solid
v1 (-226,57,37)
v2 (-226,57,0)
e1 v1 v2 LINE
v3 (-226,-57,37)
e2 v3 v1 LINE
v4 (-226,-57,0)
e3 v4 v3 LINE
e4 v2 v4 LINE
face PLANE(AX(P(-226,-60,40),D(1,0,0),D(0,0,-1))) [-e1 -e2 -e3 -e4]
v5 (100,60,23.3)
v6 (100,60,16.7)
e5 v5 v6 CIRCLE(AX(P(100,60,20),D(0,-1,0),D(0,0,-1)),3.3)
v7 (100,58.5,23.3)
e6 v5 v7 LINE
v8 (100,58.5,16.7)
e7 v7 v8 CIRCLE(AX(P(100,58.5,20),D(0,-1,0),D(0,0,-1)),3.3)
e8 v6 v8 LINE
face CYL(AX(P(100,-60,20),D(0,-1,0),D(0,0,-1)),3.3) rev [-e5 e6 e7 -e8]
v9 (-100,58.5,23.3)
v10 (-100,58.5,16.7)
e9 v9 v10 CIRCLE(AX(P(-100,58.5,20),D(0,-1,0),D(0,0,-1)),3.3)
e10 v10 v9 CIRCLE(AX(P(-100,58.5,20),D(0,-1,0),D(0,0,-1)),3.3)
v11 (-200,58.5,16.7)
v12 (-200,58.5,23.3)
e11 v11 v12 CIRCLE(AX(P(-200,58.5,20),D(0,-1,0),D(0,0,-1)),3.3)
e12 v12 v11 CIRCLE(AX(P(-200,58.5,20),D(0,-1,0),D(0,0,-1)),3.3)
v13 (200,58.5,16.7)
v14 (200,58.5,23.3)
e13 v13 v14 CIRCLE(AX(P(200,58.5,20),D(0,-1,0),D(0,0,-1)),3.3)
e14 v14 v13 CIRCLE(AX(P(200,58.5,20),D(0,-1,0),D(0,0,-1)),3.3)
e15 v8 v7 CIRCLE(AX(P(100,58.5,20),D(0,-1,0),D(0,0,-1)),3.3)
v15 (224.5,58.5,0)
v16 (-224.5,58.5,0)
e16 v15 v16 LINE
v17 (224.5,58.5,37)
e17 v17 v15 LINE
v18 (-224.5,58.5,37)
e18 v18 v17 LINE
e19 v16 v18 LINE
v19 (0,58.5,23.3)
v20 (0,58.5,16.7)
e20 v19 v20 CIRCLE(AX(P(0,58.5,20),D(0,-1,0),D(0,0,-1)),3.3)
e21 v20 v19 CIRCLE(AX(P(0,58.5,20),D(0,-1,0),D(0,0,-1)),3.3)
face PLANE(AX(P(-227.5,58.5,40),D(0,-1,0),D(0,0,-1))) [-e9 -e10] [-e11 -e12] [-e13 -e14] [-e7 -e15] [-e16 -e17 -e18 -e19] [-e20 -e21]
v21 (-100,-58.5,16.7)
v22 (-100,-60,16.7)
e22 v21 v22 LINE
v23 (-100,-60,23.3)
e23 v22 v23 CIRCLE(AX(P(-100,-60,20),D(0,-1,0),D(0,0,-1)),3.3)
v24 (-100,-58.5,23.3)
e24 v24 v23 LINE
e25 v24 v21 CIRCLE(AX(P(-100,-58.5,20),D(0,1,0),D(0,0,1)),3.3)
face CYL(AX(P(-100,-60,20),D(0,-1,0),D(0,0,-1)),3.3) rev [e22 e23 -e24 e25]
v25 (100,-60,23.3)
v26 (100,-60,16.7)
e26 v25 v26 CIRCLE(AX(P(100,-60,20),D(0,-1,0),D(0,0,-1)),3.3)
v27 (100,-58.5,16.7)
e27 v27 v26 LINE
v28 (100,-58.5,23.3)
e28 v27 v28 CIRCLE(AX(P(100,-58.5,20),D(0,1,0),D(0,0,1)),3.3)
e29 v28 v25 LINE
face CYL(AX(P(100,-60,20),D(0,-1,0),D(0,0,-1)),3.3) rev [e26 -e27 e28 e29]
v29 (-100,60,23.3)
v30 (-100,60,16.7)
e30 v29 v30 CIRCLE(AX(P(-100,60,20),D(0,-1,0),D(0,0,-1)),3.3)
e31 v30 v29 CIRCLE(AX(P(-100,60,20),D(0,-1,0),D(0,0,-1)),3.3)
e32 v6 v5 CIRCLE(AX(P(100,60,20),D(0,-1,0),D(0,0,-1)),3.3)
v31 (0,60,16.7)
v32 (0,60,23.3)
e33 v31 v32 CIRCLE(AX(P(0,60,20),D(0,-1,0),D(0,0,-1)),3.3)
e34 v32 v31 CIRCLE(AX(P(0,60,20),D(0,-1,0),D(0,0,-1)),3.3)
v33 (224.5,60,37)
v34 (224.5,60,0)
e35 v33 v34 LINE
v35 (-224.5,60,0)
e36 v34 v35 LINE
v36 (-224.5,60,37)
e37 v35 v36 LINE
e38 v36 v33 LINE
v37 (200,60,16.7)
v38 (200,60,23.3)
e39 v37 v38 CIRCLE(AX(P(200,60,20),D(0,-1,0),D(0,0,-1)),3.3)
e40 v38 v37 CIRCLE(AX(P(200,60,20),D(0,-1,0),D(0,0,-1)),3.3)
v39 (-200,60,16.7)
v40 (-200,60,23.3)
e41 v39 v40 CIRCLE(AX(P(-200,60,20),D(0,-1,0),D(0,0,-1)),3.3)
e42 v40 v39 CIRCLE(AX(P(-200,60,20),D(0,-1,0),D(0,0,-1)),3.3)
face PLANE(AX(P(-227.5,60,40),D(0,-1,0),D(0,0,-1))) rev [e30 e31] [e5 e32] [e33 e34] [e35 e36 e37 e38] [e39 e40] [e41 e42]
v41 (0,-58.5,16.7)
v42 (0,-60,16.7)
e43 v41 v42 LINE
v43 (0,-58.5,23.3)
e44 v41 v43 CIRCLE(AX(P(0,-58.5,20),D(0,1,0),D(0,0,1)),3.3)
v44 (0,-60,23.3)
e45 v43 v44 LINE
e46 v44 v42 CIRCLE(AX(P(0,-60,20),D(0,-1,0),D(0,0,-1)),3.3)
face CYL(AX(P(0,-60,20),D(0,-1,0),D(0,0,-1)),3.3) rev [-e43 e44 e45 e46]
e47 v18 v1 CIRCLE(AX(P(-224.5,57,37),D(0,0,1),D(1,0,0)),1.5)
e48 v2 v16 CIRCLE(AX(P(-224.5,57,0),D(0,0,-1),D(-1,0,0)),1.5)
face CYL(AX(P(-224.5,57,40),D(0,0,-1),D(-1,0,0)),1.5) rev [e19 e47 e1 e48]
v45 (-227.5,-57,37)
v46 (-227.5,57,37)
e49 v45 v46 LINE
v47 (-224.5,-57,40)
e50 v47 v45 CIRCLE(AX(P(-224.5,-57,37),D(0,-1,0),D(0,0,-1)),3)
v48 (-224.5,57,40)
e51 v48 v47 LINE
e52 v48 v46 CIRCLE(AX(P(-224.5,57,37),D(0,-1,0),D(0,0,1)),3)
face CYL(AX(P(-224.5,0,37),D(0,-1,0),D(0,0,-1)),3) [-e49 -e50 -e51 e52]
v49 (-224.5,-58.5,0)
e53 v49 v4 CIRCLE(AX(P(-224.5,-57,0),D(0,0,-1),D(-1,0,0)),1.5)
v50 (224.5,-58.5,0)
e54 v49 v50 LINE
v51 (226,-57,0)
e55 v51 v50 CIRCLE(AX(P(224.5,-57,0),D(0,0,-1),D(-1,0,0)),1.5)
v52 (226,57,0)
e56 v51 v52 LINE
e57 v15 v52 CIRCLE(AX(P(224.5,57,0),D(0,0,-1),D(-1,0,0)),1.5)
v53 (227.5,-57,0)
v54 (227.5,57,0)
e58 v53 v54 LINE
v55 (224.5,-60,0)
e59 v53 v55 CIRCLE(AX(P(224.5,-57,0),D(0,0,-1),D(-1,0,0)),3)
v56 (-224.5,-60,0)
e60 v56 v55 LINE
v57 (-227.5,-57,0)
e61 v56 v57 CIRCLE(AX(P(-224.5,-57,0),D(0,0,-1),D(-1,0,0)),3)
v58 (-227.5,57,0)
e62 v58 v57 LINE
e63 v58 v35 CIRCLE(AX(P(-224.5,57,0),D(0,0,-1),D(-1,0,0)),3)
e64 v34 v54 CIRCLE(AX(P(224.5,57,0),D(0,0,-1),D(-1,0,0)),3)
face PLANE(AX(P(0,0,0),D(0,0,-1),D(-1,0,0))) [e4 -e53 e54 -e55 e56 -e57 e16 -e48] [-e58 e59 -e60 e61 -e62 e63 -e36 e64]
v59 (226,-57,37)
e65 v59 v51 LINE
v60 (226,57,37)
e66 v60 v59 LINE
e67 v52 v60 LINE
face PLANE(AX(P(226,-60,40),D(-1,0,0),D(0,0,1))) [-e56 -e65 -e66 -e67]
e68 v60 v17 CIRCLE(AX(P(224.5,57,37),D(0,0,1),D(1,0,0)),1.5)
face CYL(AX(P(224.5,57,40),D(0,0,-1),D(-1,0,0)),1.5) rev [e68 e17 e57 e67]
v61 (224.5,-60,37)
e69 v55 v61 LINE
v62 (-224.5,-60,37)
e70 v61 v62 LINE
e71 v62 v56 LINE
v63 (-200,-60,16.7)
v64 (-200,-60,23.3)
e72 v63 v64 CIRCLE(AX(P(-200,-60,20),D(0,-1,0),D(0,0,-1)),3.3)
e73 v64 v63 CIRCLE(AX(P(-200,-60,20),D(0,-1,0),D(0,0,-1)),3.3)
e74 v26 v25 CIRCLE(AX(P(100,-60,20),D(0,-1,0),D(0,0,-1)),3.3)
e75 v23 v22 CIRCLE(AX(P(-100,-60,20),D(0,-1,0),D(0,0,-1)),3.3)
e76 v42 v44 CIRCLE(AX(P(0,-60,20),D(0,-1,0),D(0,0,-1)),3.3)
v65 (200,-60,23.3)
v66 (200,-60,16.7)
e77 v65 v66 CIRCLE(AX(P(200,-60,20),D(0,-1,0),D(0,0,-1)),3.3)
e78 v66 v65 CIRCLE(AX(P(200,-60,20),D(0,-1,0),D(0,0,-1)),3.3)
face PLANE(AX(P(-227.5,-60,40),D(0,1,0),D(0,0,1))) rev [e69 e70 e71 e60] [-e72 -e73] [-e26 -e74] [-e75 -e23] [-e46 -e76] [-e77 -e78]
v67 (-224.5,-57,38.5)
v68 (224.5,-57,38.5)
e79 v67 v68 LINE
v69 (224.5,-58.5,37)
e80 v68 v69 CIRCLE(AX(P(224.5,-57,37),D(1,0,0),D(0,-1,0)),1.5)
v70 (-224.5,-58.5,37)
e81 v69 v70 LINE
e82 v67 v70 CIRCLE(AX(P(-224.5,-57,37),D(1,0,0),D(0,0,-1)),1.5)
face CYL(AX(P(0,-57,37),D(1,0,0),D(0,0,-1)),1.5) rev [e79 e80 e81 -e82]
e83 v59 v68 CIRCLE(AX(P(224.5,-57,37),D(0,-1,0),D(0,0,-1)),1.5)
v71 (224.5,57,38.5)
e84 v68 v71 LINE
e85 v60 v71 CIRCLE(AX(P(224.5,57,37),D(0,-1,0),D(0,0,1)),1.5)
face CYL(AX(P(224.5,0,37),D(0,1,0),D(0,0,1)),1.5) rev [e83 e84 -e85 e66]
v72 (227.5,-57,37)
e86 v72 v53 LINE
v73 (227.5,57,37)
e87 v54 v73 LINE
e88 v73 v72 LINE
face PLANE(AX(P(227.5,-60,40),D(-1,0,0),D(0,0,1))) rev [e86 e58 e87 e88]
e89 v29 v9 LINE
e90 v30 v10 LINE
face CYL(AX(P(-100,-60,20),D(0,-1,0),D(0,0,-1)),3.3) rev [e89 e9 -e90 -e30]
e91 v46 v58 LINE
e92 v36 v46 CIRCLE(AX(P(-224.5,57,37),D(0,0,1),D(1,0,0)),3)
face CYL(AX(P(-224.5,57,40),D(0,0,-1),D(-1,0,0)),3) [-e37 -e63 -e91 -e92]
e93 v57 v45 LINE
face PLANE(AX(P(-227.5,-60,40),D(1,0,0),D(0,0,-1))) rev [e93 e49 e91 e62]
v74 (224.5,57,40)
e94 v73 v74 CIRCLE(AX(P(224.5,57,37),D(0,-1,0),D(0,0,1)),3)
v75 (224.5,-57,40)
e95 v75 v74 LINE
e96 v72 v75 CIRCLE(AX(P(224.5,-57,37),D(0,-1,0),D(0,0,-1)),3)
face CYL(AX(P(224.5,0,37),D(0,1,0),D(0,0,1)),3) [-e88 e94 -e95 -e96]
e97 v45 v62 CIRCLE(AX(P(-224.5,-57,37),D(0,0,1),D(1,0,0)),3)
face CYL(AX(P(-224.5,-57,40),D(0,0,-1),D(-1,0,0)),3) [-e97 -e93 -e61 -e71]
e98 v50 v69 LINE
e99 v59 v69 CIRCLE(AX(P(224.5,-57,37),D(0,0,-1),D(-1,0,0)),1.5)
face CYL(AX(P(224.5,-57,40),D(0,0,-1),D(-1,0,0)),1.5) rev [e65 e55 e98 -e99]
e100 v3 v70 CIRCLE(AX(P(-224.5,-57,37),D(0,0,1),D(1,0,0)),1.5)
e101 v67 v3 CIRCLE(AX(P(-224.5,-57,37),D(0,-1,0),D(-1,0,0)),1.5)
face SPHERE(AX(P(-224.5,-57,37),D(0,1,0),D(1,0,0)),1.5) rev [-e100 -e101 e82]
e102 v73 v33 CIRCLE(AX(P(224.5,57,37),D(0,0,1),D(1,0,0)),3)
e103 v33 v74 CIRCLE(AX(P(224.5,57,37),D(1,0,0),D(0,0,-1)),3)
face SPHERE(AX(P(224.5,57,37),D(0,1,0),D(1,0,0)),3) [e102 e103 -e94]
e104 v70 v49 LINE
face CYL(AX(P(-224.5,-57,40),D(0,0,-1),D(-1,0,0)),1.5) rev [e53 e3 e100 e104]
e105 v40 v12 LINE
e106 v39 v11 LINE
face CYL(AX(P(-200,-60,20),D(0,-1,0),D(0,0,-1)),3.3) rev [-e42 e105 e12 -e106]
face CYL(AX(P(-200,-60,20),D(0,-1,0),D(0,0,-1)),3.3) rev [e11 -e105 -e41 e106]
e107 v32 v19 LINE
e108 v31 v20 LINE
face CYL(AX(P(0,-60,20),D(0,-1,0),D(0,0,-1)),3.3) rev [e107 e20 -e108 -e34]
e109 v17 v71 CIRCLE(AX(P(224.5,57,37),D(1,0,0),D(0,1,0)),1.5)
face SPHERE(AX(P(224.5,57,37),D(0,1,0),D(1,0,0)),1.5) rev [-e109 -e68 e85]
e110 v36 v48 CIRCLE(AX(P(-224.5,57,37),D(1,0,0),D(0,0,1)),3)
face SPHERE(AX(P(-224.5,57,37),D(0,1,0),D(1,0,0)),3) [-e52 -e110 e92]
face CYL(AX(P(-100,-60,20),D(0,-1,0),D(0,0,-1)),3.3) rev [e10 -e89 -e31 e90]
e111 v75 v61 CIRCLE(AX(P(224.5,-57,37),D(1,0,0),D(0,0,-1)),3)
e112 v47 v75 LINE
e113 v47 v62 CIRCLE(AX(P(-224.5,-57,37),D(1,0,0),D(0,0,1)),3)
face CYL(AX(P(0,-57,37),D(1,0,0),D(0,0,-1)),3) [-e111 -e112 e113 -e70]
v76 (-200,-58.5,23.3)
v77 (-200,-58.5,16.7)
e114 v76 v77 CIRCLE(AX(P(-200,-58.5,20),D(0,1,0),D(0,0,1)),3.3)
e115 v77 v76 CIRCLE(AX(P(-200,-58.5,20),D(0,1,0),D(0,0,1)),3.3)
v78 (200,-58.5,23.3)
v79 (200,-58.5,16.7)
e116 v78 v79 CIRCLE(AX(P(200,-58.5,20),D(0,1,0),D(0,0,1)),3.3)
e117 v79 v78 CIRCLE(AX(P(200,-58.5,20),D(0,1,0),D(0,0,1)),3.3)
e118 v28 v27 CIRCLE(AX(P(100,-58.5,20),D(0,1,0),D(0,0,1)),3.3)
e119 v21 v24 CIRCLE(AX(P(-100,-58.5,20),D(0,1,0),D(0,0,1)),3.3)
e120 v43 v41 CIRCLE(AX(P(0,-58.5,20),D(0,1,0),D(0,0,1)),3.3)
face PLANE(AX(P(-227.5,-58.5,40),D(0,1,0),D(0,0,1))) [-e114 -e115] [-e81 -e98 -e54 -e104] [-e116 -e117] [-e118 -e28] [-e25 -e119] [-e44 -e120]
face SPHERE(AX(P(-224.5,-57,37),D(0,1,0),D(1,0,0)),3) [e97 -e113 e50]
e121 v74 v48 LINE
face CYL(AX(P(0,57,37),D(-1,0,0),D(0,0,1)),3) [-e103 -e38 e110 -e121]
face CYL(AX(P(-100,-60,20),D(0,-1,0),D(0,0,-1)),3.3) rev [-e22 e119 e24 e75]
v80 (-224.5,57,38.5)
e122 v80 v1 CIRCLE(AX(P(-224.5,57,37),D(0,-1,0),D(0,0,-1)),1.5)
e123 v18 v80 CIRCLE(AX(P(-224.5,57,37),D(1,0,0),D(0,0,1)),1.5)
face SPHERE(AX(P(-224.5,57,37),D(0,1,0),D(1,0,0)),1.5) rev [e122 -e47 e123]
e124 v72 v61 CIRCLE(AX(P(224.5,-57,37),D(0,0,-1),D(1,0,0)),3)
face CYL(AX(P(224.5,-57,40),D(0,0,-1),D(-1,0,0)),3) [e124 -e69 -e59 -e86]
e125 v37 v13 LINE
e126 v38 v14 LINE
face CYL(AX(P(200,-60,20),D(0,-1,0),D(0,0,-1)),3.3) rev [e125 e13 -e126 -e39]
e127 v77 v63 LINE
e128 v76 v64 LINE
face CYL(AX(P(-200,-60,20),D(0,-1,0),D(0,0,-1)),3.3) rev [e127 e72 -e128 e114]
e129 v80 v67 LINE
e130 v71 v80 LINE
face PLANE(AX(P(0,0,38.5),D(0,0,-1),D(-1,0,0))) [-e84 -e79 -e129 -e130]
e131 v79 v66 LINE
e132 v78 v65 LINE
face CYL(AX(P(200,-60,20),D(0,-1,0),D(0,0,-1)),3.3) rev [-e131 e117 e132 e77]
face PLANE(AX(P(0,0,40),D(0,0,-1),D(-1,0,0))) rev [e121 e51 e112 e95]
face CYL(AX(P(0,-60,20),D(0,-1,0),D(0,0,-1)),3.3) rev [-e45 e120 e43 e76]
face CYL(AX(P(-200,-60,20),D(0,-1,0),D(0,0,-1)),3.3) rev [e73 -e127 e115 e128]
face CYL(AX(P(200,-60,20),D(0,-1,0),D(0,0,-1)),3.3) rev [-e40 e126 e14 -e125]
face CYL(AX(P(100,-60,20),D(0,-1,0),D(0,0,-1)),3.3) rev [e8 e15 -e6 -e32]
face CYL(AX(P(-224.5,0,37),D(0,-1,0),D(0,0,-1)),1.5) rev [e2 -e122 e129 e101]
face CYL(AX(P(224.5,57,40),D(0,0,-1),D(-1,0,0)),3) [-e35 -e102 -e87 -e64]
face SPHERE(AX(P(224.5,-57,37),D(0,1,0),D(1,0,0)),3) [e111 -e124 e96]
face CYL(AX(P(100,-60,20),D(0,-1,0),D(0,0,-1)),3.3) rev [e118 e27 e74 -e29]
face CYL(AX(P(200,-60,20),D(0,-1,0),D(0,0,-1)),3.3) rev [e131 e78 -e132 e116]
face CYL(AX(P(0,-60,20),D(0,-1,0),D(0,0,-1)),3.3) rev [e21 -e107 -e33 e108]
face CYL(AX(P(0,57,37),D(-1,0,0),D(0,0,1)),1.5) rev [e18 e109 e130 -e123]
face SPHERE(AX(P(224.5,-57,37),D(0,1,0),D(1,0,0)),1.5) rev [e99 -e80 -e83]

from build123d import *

# Parameters (mm, degrees)
SKETCH_1_W         = 455
SKETCH_1_H         = 120
EXTRUDE_1_DEPTH    = 40
FILLET_1_R         = 3
SHELL_1_T          = -1.5
HOLE_WIZARD_M6_1_D = 6.6


with BuildPart() as part:
    # 草图1 → 凸台-拉伸1 (new body)
    with BuildSketch(Plane.XY):
        Rectangle(SKETCH_1_W, SKETCH_1_H)
    extrude(amount=EXTRUDE_1_DEPTH)

    # 圆角1
    fillet_1_edges = [part.edges().sort_by_distance(p)[0] for p in [
        (-227.5, 0, 40),
        (0, -60, 40),
        (227.5, 0, 40),
        (0, 60, 40),
        (227.5, -60, 20),
        (-227.5, -60, 20),
        (-227.5, 60, 20),
        (227.5, 60, 20),
    ]]
    fillet(fillet_1_edges, radius=FILLET_1_R)

    # 抽壳1
    shell_1_openings = [part.faces().sort_by_distance(p)[0] for p in [
        (0, 0, 0),
    ]]
    offset(amount=SHELL_1_T, openings=shell_1_openings, kind=Kind.INTERSECTION)

    # M6 间隙孔1 (through all)
    with Locations(Plane(origin=(0, -60, 0), x_dir=(-1, 0, 0), z_dir=(0, -1, 0))):
        with Locations((200, -20), (100, -20), (-100, -20), (-200, -20), (0, -20)):
            Hole(HOLE_WIZARD_M6_1_D / 2)


solid = part.part
